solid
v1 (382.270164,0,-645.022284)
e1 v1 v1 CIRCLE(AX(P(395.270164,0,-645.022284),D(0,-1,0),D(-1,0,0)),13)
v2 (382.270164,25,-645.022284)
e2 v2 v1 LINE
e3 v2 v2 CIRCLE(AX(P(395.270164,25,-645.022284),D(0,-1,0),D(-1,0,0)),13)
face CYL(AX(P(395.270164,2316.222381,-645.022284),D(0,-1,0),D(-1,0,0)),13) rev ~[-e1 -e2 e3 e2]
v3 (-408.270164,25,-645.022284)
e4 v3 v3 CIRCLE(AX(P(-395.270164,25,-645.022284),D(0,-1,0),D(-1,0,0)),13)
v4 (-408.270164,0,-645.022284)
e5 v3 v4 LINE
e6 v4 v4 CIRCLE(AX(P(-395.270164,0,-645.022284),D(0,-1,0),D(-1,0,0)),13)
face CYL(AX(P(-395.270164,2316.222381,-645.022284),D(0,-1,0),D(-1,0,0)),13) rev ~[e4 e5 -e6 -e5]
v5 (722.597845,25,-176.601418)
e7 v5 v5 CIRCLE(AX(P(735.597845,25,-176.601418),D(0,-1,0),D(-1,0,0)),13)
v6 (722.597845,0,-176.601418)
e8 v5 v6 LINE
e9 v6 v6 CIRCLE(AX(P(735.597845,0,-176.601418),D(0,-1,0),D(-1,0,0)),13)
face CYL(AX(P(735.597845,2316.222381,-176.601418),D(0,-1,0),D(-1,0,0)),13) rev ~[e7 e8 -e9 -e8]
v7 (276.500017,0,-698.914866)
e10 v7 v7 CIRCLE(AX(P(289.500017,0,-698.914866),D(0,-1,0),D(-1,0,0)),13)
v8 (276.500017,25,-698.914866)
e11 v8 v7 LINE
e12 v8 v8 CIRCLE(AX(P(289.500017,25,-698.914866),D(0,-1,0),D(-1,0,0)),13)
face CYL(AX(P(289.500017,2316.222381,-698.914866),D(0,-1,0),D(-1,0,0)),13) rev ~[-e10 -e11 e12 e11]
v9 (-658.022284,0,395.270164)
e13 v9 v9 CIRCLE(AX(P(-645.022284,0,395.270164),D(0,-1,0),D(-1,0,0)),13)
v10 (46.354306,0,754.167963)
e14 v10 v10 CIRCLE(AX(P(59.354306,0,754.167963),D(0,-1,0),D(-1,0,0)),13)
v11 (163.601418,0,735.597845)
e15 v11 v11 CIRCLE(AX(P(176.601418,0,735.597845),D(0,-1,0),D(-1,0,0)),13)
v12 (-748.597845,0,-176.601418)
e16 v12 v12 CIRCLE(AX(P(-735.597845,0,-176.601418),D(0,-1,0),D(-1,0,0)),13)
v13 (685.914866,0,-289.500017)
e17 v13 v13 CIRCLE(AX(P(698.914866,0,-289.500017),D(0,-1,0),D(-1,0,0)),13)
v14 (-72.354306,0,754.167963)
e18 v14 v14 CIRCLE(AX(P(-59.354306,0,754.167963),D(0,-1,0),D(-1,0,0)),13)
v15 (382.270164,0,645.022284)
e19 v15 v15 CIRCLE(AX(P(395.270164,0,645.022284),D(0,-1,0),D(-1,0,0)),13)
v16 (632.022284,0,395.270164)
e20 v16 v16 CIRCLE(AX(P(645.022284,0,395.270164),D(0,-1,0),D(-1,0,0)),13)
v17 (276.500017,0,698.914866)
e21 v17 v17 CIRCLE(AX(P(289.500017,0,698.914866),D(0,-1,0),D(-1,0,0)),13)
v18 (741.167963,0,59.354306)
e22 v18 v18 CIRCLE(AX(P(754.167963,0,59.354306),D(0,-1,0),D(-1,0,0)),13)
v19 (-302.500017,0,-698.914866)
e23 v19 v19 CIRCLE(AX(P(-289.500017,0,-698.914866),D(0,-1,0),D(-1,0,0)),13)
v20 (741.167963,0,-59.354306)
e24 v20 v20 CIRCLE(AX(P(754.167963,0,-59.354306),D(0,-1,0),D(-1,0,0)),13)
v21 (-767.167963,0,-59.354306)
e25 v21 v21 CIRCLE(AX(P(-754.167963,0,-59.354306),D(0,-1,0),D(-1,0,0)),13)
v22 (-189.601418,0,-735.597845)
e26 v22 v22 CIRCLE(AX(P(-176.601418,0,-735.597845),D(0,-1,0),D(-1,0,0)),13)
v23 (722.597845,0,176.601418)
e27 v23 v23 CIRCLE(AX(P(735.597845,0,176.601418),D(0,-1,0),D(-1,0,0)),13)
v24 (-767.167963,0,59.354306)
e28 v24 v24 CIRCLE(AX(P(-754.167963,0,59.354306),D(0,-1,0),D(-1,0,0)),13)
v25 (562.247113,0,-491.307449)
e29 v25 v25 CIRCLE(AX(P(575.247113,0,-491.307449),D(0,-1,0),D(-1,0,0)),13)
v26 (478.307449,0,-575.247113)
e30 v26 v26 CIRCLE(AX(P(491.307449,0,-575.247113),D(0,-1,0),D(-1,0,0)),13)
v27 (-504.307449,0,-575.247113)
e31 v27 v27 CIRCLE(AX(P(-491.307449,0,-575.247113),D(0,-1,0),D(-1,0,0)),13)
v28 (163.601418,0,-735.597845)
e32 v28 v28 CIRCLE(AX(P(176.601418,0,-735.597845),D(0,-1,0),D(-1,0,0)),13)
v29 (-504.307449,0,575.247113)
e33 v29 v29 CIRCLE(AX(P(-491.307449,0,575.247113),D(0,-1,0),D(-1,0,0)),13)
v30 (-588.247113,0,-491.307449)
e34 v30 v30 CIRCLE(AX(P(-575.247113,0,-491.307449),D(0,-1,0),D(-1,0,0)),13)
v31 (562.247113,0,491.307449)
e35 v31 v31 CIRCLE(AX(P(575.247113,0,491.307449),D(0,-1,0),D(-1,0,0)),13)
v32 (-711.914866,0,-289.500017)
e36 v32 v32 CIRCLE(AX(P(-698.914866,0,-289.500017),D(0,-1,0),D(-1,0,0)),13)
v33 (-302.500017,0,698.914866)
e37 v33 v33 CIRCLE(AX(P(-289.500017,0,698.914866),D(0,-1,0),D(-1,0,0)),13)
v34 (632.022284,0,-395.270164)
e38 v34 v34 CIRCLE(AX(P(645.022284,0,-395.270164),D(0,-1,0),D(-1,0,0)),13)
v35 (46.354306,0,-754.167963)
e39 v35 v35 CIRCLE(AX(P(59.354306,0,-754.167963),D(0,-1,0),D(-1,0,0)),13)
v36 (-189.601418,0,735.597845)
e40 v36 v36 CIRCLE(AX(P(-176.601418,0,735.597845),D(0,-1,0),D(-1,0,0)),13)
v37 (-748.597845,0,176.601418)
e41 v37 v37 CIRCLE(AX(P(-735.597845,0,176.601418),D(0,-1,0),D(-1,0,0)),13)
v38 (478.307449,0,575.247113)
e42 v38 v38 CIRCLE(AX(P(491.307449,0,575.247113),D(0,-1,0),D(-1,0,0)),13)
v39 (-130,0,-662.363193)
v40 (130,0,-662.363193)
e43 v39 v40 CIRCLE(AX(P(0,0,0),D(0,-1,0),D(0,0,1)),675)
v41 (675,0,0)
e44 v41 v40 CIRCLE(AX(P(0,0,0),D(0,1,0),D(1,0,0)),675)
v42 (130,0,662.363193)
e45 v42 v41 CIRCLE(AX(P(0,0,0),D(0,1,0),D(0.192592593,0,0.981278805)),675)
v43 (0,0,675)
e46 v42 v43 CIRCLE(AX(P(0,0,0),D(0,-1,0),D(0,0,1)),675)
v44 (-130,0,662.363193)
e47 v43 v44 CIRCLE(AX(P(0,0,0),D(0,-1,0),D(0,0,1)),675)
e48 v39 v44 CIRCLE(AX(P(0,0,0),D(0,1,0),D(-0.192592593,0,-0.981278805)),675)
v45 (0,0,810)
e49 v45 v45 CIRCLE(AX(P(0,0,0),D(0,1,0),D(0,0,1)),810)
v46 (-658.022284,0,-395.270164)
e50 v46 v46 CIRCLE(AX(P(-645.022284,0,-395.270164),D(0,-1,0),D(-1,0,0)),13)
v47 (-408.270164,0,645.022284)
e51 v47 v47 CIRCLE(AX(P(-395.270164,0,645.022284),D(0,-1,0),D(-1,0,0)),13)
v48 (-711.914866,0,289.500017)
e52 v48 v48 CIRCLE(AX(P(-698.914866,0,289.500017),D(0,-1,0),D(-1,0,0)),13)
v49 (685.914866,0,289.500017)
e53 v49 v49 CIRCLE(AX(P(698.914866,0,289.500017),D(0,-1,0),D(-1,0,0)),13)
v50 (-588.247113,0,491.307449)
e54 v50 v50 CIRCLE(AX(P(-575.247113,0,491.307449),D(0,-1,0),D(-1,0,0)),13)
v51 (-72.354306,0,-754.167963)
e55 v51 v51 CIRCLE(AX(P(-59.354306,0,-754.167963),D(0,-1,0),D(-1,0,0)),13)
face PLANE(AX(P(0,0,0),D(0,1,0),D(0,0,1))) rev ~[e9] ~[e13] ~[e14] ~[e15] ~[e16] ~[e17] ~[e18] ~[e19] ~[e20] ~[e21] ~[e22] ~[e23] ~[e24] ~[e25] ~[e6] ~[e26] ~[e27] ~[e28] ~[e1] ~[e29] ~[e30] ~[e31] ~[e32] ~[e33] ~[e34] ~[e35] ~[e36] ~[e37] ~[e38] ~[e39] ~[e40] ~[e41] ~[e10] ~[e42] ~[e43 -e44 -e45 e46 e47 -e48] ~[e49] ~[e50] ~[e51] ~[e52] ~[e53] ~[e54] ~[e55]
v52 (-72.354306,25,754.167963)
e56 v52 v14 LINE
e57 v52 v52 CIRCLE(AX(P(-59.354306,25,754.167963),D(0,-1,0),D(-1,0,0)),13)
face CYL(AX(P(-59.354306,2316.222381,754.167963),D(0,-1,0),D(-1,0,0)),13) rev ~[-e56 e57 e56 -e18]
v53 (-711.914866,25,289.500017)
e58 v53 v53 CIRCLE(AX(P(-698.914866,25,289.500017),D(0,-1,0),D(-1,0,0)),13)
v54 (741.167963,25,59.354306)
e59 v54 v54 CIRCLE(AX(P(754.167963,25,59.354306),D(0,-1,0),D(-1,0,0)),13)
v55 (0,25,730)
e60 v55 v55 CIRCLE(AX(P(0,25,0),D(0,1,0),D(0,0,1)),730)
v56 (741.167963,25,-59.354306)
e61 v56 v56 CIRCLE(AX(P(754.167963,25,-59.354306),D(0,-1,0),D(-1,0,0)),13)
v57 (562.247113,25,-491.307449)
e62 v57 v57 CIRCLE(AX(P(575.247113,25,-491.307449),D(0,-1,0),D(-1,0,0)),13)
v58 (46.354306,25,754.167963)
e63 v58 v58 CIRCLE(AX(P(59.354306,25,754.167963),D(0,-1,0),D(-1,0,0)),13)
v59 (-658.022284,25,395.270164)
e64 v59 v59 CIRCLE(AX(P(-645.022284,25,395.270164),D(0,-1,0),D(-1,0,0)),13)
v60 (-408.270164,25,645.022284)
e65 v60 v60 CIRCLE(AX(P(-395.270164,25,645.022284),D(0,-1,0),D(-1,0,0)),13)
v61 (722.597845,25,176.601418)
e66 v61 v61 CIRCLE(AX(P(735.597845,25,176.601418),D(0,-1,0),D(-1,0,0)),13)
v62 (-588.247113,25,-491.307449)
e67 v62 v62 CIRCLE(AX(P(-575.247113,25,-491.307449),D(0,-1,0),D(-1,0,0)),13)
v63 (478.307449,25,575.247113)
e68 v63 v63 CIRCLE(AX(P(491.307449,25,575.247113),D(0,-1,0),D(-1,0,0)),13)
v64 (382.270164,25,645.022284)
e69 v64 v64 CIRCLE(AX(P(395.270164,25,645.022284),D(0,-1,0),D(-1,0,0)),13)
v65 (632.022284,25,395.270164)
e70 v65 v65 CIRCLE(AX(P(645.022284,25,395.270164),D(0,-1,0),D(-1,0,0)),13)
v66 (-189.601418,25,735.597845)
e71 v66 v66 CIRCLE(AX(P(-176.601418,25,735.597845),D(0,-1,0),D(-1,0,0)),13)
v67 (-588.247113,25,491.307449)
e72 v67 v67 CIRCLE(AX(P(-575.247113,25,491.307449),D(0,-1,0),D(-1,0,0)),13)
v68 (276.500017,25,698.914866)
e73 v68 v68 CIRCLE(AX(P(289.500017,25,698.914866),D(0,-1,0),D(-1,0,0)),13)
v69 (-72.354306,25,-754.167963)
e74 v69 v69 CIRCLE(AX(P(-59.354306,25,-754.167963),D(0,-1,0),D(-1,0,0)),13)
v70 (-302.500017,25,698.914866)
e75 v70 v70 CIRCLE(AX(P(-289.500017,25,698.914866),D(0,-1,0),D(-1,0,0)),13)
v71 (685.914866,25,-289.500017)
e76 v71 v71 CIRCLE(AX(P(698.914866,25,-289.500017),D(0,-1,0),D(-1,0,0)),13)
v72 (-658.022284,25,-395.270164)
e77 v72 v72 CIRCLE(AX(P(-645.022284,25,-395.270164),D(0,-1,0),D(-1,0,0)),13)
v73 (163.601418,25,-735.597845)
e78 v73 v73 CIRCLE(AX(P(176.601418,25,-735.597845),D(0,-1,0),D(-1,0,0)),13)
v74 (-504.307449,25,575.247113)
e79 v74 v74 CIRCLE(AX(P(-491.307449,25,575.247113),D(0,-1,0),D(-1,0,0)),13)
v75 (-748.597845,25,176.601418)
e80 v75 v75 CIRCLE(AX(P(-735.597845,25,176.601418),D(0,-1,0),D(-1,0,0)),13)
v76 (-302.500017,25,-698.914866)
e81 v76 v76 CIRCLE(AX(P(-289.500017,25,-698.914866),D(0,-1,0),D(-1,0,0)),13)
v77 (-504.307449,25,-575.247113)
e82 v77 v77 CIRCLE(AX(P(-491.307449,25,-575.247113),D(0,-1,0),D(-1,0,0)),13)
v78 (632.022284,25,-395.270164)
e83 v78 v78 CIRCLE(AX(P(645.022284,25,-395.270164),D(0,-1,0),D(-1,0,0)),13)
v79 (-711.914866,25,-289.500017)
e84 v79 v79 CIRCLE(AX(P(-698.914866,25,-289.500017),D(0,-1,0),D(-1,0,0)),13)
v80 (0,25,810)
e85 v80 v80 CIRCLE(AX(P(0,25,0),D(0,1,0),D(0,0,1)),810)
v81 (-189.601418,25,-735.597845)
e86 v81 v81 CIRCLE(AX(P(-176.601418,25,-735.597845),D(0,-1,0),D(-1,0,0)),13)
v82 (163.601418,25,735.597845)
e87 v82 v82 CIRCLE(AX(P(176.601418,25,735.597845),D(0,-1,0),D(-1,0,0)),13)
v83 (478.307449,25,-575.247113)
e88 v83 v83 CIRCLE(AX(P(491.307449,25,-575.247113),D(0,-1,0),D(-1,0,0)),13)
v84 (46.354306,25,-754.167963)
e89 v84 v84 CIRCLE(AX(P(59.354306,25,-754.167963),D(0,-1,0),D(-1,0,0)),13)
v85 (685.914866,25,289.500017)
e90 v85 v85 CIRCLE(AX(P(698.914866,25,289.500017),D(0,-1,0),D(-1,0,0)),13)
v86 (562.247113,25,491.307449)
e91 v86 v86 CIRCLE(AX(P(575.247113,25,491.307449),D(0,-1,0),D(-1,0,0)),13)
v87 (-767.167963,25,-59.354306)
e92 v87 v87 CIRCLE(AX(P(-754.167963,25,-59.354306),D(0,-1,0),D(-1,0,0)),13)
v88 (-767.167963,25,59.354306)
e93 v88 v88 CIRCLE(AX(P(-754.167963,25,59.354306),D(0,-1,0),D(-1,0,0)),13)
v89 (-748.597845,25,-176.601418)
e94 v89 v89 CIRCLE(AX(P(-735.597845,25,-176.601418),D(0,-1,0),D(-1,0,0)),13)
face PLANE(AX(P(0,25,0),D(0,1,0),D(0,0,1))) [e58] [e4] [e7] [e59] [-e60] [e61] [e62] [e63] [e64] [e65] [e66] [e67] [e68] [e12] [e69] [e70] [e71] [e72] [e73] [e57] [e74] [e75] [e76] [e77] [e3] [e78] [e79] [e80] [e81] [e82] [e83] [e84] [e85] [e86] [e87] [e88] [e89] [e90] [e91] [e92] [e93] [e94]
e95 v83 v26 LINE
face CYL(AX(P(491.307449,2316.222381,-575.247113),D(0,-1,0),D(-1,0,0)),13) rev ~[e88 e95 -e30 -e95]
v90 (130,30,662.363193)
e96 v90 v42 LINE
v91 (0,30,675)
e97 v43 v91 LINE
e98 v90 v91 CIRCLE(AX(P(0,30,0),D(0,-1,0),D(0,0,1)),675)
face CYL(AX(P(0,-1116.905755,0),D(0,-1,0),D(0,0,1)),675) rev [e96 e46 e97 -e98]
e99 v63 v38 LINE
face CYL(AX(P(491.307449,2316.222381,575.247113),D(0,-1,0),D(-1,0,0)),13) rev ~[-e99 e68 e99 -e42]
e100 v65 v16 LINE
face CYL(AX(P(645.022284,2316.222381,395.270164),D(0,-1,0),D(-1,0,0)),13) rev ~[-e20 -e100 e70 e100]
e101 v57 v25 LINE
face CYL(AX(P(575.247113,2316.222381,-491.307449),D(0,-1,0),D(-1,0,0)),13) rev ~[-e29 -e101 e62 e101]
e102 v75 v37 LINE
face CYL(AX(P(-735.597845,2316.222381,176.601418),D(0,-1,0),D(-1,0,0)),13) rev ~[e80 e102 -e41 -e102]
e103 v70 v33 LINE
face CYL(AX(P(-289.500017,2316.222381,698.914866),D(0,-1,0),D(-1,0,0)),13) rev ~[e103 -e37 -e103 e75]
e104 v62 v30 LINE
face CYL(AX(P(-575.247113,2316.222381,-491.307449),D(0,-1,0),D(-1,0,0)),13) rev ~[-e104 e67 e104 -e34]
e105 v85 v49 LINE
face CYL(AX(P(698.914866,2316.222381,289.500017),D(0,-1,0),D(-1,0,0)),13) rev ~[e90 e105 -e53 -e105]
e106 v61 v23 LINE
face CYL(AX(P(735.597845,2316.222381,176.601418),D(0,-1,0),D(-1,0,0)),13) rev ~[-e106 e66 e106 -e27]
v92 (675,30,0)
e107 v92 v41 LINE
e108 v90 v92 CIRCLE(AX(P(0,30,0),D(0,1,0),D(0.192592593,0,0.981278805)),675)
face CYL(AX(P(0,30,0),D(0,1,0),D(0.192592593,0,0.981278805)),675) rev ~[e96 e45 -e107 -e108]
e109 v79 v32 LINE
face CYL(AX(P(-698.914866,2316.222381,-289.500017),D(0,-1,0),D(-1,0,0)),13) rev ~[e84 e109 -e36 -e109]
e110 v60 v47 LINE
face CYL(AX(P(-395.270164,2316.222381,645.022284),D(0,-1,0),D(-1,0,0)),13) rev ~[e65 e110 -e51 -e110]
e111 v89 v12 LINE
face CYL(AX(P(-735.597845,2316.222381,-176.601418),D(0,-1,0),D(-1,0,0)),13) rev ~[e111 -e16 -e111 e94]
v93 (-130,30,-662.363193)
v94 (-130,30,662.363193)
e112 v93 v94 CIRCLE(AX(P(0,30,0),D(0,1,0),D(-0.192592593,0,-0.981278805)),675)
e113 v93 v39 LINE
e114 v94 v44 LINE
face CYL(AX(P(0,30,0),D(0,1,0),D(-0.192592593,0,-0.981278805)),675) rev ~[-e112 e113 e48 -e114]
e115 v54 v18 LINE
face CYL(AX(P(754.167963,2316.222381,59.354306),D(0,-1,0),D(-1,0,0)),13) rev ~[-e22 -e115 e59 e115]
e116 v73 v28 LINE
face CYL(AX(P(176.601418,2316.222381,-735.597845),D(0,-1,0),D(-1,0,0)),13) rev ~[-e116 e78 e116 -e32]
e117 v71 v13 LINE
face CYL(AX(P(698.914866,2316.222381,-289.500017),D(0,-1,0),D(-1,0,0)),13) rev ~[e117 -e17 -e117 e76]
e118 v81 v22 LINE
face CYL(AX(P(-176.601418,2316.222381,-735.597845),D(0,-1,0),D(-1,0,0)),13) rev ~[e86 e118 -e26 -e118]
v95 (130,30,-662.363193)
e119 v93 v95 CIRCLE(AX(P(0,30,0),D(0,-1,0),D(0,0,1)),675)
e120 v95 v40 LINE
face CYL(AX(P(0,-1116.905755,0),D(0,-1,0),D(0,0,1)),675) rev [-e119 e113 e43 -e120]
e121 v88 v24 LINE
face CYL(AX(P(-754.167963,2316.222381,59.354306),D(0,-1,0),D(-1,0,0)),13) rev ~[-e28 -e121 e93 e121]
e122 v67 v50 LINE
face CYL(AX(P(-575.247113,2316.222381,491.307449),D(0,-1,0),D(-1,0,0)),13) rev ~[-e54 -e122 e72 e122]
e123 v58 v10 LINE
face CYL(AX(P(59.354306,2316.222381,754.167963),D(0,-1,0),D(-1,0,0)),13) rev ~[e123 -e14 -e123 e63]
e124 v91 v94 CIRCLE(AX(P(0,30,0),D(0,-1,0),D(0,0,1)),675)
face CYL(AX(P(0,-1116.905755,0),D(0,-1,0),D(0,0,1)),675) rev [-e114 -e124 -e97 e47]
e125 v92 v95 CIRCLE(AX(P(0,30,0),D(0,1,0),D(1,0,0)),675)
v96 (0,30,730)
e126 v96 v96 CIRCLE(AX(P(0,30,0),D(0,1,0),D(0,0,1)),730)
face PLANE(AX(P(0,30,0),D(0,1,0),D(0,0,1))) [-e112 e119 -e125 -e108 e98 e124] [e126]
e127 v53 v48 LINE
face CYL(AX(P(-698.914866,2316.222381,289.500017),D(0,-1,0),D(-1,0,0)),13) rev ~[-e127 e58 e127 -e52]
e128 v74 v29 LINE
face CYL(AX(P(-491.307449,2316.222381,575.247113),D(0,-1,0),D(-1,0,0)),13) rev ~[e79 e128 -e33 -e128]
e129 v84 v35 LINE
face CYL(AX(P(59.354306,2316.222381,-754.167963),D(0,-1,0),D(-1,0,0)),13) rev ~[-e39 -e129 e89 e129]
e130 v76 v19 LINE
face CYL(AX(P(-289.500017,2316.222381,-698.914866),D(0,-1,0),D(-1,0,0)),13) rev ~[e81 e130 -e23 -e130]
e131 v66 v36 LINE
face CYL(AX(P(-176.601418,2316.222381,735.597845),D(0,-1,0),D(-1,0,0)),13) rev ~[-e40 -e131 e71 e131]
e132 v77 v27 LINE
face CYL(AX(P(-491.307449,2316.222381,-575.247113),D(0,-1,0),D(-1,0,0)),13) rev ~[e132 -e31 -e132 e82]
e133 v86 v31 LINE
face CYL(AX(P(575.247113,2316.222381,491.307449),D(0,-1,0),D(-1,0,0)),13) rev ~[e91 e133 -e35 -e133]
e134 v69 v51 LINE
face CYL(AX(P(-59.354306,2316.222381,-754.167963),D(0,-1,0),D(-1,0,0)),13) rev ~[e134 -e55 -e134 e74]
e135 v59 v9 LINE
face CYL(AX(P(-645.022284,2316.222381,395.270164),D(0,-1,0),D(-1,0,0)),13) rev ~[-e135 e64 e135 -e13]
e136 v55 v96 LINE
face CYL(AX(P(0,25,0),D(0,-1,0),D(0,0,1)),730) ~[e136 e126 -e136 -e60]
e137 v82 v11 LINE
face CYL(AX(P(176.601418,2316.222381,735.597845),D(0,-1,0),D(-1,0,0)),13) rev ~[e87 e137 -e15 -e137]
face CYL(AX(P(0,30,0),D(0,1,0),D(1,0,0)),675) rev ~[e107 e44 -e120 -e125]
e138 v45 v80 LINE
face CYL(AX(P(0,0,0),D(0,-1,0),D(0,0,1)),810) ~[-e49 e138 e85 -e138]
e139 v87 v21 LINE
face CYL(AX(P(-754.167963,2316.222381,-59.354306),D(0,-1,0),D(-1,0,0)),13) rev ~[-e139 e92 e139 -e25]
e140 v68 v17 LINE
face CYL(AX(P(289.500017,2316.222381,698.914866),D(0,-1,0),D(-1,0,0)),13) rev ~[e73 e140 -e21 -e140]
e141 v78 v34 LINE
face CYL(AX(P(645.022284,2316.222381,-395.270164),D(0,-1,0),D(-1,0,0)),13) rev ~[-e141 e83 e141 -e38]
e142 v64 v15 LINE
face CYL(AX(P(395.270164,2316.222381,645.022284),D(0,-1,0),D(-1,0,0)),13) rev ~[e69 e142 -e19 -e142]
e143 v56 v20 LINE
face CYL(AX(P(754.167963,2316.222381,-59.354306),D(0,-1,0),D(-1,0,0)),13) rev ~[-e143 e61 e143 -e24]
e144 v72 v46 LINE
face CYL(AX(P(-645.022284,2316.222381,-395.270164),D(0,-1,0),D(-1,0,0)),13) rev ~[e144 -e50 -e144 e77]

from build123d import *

# Parameters (mm, degrees)
SKETCH_1_R                = 810
EXTRUDE_1_DEPTH           = 25
SKETCH_2_R                = 730
EXTRUDE_2_DEPTH           = 5
CUT_EXTRUDE_1_REACH       = 1147.906
SKETCH_3_R                = 75
SKETCH_4_R                = 110
CUT_EXTRUDE_2_DEPTH       = 5
HOLE_WIZARD_M8_1_D        = 6.8
HOLE_WIZARD_25_5_25_5_1_D = 26
CUT_EXTRUDE_3_DEPTH       = 1146.905755287
CUT_EXTRUDE_3_DEPTH_BACK  = 1146.905755287
SKETCH_10_R               = 675


with BuildPart() as part:
    # 草图1 → 凸台-拉伸1 (new body)
    with BuildSketch(Plane(origin=(0, 0, 0), x_dir=(1, 0, 0), z_dir=(0, 1, 0))):
        with Locations(Location((0, 0, 0), (0, 0, 270))):
            Circle(SKETCH_1_R)
    extrude(amount=EXTRUDE_1_DEPTH)

    # 草图2 → 凸台-拉伸2 (add)
    with BuildSketch(Plane(origin=(0, 25, 0), x_dir=(1, 0, 0), z_dir=(0, 1, 0))):
        with Locations(Location((0, 0, 0), (0, 0, 270))):
            Circle(SKETCH_2_R)
    extrude(amount=EXTRUDE_2_DEPTH)

    # 草图3 → 切除-拉伸1 (cut, up to next)
    with BuildSketch(Plane(origin=(0, 30, 0), x_dir=(1, 0, 0), z_dir=(0, 1, 0)), mode=Mode.PRIVATE) as cut_extrude_1_sk1:
        with BuildLine():
            Line((130, 662.363193422), (130, -662.363193422))
            ThreePointArc((130, -662.363193422), (521.236510617, -428.879353665), (675, 0))
            ThreePointArc((675, 0), (521.236510617, 428.879353665), (130, 662.363193422))
        make_face()
    cut_extrude_1_tool1 = extrude(cut_extrude_1_sk1.sketch, amount=-CUT_EXTRUDE_1_REACH, mode=Mode.PRIVATE) & part.part
    # 草图3 → 切除-拉伸1 (cut, up to next)
    with BuildSketch(Plane(origin=(0, 30, 0), x_dir=(1, 0, 0), z_dir=(0, 1, 0)), mode=Mode.PRIVATE) as cut_extrude_1_sk2:
        with BuildLine():
            ThreePointArc((-130, 662.363193422), (-675, 0), (-130, -662.363193422))
            Line((-130, -662.363193422), (-130, 662.363193422))
        make_face()
    cut_extrude_1_tool2 = extrude(cut_extrude_1_sk2.sketch, amount=-CUT_EXTRUDE_1_REACH, mode=Mode.PRIVATE) & part.part
    # 草图3 → 切除-拉伸1 (cut, up to next)
    with BuildSketch(Plane(origin=(0, 30, 0), x_dir=(1, 0, 0), z_dir=(0, 1, 0)), mode=Mode.PRIVATE) as cut_extrude_1_sk3:
        with Locations(Location((0, 0, 0), (0, 0, 270))):
            Circle(SKETCH_3_R)
    cut_extrude_1_tool3 = extrude(cut_extrude_1_sk3.sketch, amount=-CUT_EXTRUDE_1_REACH, mode=Mode.PRIVATE) & part.part
    add(cut_extrude_1_tool1.solids().sort_by_distance((357.907844, 30, 0))[0], mode=Mode.SUBTRACT)
    add(cut_extrude_1_tool2.solids().sort_by_distance((-357.907844, 30, 0))[0], mode=Mode.SUBTRACT)
    add(cut_extrude_1_tool3.solids().sort_by_distance((0, 30, 0))[0], mode=Mode.SUBTRACT)

    # 草图4 → 切除-拉伸2 (cut)
    with BuildSketch(Plane(origin=(0, 30, 0), x_dir=(1, 0, 0), z_dir=(0, 1, 0))):
        with Locations(Location((0, 0, 0), (0, 0, 270))):
            Circle(SKETCH_4_R)
    extrude(amount=-CUT_EXTRUDE_2_DEPTH, mode=Mode.SUBTRACT)

    # M8 螺纹孔1 (through all)
    with Locations(Plane(origin=(0, 25, 0), x_dir=(1, 0, 0), z_dir=(0, 1, 0))):
        with Locations((0, 85), (85, 0), (0, -85), (-85, 0)):
            Hole(HOLE_WIZARD_M8_1_D / 2)

    # Ø25.5 (25.5) 直径孔1 (through all)
    with Locations(Plane(origin=(0, 25, 0), x_dir=(1, 0, 0), z_dir=(0, 1, 0))):
        with Locations((-59.354305918, 754.167962969), (59.354305918, 754.167962969), (176.601417757, 735.597844781), (289.500016584, 698.914866345), (395.270164208, 645.022284334), (491.307448562, 575.247112976), (575.247112976, 491.307448562), (645.022284334, 395.270164208), (698.914866345, 289.500016584), (735.597844781, 176.601417757), (754.167962969, 59.354305918), (754.167962969, -59.354305918), (735.597844781, -176.601417757), (698.914866345, -289.500016584), (645.022284334, -395.270164208), (575.247112976, -491.307448562), (491.307448562, -575.247112976), (395.270164208, -645.022284334), (289.500016584, -698.914866345), (176.601417757, -735.597844781), (59.354305918, -754.167962969), (-59.354305918, -754.167962969), (-176.601417757, -735.597844781), (-289.500016584, -698.914866345), (-395.270164208, -645.022284334), (-491.307448562, -575.247112976), (-575.247112976, -491.307448562), (-645.022284334, -395.270164208), (-698.914866345, -289.500016584), (-735.597844781, -176.601417757), (-754.167962969, -59.354305918), (-754.167962969, 59.354305918), (-735.597844781, 176.601417757), (-698.914866345, 289.500016584), (-645.022284334, 395.270164208), (-575.247112976, 491.307448562), (-491.307448562, 575.247112976), (-395.270164208, 645.022284334), (-289.500016584, 698.914866345), (-176.601417757, 735.597844781)):
            Hole(HOLE_WIZARD_25_5_25_5_1_D / 2)

    # 草图10 → 切除-拉伸3 (cut, two sides: drawn at the far end of the back side and taken through both)
    with BuildSketch(Plane(origin=(0, 30, 0), x_dir=(1, 0, 0), z_dir=(0, 1, 0)).offset(-CUT_EXTRUDE_3_DEPTH_BACK)):
        with Locations(Location((0, 0, 0), (0, 0, 270))):
            Circle(SKETCH_10_R)
    extrude(amount=CUT_EXTRUDE_3_DEPTH + CUT_EXTRUDE_3_DEPTH_BACK, mode=Mode.SUBTRACT)


solid = part.part
